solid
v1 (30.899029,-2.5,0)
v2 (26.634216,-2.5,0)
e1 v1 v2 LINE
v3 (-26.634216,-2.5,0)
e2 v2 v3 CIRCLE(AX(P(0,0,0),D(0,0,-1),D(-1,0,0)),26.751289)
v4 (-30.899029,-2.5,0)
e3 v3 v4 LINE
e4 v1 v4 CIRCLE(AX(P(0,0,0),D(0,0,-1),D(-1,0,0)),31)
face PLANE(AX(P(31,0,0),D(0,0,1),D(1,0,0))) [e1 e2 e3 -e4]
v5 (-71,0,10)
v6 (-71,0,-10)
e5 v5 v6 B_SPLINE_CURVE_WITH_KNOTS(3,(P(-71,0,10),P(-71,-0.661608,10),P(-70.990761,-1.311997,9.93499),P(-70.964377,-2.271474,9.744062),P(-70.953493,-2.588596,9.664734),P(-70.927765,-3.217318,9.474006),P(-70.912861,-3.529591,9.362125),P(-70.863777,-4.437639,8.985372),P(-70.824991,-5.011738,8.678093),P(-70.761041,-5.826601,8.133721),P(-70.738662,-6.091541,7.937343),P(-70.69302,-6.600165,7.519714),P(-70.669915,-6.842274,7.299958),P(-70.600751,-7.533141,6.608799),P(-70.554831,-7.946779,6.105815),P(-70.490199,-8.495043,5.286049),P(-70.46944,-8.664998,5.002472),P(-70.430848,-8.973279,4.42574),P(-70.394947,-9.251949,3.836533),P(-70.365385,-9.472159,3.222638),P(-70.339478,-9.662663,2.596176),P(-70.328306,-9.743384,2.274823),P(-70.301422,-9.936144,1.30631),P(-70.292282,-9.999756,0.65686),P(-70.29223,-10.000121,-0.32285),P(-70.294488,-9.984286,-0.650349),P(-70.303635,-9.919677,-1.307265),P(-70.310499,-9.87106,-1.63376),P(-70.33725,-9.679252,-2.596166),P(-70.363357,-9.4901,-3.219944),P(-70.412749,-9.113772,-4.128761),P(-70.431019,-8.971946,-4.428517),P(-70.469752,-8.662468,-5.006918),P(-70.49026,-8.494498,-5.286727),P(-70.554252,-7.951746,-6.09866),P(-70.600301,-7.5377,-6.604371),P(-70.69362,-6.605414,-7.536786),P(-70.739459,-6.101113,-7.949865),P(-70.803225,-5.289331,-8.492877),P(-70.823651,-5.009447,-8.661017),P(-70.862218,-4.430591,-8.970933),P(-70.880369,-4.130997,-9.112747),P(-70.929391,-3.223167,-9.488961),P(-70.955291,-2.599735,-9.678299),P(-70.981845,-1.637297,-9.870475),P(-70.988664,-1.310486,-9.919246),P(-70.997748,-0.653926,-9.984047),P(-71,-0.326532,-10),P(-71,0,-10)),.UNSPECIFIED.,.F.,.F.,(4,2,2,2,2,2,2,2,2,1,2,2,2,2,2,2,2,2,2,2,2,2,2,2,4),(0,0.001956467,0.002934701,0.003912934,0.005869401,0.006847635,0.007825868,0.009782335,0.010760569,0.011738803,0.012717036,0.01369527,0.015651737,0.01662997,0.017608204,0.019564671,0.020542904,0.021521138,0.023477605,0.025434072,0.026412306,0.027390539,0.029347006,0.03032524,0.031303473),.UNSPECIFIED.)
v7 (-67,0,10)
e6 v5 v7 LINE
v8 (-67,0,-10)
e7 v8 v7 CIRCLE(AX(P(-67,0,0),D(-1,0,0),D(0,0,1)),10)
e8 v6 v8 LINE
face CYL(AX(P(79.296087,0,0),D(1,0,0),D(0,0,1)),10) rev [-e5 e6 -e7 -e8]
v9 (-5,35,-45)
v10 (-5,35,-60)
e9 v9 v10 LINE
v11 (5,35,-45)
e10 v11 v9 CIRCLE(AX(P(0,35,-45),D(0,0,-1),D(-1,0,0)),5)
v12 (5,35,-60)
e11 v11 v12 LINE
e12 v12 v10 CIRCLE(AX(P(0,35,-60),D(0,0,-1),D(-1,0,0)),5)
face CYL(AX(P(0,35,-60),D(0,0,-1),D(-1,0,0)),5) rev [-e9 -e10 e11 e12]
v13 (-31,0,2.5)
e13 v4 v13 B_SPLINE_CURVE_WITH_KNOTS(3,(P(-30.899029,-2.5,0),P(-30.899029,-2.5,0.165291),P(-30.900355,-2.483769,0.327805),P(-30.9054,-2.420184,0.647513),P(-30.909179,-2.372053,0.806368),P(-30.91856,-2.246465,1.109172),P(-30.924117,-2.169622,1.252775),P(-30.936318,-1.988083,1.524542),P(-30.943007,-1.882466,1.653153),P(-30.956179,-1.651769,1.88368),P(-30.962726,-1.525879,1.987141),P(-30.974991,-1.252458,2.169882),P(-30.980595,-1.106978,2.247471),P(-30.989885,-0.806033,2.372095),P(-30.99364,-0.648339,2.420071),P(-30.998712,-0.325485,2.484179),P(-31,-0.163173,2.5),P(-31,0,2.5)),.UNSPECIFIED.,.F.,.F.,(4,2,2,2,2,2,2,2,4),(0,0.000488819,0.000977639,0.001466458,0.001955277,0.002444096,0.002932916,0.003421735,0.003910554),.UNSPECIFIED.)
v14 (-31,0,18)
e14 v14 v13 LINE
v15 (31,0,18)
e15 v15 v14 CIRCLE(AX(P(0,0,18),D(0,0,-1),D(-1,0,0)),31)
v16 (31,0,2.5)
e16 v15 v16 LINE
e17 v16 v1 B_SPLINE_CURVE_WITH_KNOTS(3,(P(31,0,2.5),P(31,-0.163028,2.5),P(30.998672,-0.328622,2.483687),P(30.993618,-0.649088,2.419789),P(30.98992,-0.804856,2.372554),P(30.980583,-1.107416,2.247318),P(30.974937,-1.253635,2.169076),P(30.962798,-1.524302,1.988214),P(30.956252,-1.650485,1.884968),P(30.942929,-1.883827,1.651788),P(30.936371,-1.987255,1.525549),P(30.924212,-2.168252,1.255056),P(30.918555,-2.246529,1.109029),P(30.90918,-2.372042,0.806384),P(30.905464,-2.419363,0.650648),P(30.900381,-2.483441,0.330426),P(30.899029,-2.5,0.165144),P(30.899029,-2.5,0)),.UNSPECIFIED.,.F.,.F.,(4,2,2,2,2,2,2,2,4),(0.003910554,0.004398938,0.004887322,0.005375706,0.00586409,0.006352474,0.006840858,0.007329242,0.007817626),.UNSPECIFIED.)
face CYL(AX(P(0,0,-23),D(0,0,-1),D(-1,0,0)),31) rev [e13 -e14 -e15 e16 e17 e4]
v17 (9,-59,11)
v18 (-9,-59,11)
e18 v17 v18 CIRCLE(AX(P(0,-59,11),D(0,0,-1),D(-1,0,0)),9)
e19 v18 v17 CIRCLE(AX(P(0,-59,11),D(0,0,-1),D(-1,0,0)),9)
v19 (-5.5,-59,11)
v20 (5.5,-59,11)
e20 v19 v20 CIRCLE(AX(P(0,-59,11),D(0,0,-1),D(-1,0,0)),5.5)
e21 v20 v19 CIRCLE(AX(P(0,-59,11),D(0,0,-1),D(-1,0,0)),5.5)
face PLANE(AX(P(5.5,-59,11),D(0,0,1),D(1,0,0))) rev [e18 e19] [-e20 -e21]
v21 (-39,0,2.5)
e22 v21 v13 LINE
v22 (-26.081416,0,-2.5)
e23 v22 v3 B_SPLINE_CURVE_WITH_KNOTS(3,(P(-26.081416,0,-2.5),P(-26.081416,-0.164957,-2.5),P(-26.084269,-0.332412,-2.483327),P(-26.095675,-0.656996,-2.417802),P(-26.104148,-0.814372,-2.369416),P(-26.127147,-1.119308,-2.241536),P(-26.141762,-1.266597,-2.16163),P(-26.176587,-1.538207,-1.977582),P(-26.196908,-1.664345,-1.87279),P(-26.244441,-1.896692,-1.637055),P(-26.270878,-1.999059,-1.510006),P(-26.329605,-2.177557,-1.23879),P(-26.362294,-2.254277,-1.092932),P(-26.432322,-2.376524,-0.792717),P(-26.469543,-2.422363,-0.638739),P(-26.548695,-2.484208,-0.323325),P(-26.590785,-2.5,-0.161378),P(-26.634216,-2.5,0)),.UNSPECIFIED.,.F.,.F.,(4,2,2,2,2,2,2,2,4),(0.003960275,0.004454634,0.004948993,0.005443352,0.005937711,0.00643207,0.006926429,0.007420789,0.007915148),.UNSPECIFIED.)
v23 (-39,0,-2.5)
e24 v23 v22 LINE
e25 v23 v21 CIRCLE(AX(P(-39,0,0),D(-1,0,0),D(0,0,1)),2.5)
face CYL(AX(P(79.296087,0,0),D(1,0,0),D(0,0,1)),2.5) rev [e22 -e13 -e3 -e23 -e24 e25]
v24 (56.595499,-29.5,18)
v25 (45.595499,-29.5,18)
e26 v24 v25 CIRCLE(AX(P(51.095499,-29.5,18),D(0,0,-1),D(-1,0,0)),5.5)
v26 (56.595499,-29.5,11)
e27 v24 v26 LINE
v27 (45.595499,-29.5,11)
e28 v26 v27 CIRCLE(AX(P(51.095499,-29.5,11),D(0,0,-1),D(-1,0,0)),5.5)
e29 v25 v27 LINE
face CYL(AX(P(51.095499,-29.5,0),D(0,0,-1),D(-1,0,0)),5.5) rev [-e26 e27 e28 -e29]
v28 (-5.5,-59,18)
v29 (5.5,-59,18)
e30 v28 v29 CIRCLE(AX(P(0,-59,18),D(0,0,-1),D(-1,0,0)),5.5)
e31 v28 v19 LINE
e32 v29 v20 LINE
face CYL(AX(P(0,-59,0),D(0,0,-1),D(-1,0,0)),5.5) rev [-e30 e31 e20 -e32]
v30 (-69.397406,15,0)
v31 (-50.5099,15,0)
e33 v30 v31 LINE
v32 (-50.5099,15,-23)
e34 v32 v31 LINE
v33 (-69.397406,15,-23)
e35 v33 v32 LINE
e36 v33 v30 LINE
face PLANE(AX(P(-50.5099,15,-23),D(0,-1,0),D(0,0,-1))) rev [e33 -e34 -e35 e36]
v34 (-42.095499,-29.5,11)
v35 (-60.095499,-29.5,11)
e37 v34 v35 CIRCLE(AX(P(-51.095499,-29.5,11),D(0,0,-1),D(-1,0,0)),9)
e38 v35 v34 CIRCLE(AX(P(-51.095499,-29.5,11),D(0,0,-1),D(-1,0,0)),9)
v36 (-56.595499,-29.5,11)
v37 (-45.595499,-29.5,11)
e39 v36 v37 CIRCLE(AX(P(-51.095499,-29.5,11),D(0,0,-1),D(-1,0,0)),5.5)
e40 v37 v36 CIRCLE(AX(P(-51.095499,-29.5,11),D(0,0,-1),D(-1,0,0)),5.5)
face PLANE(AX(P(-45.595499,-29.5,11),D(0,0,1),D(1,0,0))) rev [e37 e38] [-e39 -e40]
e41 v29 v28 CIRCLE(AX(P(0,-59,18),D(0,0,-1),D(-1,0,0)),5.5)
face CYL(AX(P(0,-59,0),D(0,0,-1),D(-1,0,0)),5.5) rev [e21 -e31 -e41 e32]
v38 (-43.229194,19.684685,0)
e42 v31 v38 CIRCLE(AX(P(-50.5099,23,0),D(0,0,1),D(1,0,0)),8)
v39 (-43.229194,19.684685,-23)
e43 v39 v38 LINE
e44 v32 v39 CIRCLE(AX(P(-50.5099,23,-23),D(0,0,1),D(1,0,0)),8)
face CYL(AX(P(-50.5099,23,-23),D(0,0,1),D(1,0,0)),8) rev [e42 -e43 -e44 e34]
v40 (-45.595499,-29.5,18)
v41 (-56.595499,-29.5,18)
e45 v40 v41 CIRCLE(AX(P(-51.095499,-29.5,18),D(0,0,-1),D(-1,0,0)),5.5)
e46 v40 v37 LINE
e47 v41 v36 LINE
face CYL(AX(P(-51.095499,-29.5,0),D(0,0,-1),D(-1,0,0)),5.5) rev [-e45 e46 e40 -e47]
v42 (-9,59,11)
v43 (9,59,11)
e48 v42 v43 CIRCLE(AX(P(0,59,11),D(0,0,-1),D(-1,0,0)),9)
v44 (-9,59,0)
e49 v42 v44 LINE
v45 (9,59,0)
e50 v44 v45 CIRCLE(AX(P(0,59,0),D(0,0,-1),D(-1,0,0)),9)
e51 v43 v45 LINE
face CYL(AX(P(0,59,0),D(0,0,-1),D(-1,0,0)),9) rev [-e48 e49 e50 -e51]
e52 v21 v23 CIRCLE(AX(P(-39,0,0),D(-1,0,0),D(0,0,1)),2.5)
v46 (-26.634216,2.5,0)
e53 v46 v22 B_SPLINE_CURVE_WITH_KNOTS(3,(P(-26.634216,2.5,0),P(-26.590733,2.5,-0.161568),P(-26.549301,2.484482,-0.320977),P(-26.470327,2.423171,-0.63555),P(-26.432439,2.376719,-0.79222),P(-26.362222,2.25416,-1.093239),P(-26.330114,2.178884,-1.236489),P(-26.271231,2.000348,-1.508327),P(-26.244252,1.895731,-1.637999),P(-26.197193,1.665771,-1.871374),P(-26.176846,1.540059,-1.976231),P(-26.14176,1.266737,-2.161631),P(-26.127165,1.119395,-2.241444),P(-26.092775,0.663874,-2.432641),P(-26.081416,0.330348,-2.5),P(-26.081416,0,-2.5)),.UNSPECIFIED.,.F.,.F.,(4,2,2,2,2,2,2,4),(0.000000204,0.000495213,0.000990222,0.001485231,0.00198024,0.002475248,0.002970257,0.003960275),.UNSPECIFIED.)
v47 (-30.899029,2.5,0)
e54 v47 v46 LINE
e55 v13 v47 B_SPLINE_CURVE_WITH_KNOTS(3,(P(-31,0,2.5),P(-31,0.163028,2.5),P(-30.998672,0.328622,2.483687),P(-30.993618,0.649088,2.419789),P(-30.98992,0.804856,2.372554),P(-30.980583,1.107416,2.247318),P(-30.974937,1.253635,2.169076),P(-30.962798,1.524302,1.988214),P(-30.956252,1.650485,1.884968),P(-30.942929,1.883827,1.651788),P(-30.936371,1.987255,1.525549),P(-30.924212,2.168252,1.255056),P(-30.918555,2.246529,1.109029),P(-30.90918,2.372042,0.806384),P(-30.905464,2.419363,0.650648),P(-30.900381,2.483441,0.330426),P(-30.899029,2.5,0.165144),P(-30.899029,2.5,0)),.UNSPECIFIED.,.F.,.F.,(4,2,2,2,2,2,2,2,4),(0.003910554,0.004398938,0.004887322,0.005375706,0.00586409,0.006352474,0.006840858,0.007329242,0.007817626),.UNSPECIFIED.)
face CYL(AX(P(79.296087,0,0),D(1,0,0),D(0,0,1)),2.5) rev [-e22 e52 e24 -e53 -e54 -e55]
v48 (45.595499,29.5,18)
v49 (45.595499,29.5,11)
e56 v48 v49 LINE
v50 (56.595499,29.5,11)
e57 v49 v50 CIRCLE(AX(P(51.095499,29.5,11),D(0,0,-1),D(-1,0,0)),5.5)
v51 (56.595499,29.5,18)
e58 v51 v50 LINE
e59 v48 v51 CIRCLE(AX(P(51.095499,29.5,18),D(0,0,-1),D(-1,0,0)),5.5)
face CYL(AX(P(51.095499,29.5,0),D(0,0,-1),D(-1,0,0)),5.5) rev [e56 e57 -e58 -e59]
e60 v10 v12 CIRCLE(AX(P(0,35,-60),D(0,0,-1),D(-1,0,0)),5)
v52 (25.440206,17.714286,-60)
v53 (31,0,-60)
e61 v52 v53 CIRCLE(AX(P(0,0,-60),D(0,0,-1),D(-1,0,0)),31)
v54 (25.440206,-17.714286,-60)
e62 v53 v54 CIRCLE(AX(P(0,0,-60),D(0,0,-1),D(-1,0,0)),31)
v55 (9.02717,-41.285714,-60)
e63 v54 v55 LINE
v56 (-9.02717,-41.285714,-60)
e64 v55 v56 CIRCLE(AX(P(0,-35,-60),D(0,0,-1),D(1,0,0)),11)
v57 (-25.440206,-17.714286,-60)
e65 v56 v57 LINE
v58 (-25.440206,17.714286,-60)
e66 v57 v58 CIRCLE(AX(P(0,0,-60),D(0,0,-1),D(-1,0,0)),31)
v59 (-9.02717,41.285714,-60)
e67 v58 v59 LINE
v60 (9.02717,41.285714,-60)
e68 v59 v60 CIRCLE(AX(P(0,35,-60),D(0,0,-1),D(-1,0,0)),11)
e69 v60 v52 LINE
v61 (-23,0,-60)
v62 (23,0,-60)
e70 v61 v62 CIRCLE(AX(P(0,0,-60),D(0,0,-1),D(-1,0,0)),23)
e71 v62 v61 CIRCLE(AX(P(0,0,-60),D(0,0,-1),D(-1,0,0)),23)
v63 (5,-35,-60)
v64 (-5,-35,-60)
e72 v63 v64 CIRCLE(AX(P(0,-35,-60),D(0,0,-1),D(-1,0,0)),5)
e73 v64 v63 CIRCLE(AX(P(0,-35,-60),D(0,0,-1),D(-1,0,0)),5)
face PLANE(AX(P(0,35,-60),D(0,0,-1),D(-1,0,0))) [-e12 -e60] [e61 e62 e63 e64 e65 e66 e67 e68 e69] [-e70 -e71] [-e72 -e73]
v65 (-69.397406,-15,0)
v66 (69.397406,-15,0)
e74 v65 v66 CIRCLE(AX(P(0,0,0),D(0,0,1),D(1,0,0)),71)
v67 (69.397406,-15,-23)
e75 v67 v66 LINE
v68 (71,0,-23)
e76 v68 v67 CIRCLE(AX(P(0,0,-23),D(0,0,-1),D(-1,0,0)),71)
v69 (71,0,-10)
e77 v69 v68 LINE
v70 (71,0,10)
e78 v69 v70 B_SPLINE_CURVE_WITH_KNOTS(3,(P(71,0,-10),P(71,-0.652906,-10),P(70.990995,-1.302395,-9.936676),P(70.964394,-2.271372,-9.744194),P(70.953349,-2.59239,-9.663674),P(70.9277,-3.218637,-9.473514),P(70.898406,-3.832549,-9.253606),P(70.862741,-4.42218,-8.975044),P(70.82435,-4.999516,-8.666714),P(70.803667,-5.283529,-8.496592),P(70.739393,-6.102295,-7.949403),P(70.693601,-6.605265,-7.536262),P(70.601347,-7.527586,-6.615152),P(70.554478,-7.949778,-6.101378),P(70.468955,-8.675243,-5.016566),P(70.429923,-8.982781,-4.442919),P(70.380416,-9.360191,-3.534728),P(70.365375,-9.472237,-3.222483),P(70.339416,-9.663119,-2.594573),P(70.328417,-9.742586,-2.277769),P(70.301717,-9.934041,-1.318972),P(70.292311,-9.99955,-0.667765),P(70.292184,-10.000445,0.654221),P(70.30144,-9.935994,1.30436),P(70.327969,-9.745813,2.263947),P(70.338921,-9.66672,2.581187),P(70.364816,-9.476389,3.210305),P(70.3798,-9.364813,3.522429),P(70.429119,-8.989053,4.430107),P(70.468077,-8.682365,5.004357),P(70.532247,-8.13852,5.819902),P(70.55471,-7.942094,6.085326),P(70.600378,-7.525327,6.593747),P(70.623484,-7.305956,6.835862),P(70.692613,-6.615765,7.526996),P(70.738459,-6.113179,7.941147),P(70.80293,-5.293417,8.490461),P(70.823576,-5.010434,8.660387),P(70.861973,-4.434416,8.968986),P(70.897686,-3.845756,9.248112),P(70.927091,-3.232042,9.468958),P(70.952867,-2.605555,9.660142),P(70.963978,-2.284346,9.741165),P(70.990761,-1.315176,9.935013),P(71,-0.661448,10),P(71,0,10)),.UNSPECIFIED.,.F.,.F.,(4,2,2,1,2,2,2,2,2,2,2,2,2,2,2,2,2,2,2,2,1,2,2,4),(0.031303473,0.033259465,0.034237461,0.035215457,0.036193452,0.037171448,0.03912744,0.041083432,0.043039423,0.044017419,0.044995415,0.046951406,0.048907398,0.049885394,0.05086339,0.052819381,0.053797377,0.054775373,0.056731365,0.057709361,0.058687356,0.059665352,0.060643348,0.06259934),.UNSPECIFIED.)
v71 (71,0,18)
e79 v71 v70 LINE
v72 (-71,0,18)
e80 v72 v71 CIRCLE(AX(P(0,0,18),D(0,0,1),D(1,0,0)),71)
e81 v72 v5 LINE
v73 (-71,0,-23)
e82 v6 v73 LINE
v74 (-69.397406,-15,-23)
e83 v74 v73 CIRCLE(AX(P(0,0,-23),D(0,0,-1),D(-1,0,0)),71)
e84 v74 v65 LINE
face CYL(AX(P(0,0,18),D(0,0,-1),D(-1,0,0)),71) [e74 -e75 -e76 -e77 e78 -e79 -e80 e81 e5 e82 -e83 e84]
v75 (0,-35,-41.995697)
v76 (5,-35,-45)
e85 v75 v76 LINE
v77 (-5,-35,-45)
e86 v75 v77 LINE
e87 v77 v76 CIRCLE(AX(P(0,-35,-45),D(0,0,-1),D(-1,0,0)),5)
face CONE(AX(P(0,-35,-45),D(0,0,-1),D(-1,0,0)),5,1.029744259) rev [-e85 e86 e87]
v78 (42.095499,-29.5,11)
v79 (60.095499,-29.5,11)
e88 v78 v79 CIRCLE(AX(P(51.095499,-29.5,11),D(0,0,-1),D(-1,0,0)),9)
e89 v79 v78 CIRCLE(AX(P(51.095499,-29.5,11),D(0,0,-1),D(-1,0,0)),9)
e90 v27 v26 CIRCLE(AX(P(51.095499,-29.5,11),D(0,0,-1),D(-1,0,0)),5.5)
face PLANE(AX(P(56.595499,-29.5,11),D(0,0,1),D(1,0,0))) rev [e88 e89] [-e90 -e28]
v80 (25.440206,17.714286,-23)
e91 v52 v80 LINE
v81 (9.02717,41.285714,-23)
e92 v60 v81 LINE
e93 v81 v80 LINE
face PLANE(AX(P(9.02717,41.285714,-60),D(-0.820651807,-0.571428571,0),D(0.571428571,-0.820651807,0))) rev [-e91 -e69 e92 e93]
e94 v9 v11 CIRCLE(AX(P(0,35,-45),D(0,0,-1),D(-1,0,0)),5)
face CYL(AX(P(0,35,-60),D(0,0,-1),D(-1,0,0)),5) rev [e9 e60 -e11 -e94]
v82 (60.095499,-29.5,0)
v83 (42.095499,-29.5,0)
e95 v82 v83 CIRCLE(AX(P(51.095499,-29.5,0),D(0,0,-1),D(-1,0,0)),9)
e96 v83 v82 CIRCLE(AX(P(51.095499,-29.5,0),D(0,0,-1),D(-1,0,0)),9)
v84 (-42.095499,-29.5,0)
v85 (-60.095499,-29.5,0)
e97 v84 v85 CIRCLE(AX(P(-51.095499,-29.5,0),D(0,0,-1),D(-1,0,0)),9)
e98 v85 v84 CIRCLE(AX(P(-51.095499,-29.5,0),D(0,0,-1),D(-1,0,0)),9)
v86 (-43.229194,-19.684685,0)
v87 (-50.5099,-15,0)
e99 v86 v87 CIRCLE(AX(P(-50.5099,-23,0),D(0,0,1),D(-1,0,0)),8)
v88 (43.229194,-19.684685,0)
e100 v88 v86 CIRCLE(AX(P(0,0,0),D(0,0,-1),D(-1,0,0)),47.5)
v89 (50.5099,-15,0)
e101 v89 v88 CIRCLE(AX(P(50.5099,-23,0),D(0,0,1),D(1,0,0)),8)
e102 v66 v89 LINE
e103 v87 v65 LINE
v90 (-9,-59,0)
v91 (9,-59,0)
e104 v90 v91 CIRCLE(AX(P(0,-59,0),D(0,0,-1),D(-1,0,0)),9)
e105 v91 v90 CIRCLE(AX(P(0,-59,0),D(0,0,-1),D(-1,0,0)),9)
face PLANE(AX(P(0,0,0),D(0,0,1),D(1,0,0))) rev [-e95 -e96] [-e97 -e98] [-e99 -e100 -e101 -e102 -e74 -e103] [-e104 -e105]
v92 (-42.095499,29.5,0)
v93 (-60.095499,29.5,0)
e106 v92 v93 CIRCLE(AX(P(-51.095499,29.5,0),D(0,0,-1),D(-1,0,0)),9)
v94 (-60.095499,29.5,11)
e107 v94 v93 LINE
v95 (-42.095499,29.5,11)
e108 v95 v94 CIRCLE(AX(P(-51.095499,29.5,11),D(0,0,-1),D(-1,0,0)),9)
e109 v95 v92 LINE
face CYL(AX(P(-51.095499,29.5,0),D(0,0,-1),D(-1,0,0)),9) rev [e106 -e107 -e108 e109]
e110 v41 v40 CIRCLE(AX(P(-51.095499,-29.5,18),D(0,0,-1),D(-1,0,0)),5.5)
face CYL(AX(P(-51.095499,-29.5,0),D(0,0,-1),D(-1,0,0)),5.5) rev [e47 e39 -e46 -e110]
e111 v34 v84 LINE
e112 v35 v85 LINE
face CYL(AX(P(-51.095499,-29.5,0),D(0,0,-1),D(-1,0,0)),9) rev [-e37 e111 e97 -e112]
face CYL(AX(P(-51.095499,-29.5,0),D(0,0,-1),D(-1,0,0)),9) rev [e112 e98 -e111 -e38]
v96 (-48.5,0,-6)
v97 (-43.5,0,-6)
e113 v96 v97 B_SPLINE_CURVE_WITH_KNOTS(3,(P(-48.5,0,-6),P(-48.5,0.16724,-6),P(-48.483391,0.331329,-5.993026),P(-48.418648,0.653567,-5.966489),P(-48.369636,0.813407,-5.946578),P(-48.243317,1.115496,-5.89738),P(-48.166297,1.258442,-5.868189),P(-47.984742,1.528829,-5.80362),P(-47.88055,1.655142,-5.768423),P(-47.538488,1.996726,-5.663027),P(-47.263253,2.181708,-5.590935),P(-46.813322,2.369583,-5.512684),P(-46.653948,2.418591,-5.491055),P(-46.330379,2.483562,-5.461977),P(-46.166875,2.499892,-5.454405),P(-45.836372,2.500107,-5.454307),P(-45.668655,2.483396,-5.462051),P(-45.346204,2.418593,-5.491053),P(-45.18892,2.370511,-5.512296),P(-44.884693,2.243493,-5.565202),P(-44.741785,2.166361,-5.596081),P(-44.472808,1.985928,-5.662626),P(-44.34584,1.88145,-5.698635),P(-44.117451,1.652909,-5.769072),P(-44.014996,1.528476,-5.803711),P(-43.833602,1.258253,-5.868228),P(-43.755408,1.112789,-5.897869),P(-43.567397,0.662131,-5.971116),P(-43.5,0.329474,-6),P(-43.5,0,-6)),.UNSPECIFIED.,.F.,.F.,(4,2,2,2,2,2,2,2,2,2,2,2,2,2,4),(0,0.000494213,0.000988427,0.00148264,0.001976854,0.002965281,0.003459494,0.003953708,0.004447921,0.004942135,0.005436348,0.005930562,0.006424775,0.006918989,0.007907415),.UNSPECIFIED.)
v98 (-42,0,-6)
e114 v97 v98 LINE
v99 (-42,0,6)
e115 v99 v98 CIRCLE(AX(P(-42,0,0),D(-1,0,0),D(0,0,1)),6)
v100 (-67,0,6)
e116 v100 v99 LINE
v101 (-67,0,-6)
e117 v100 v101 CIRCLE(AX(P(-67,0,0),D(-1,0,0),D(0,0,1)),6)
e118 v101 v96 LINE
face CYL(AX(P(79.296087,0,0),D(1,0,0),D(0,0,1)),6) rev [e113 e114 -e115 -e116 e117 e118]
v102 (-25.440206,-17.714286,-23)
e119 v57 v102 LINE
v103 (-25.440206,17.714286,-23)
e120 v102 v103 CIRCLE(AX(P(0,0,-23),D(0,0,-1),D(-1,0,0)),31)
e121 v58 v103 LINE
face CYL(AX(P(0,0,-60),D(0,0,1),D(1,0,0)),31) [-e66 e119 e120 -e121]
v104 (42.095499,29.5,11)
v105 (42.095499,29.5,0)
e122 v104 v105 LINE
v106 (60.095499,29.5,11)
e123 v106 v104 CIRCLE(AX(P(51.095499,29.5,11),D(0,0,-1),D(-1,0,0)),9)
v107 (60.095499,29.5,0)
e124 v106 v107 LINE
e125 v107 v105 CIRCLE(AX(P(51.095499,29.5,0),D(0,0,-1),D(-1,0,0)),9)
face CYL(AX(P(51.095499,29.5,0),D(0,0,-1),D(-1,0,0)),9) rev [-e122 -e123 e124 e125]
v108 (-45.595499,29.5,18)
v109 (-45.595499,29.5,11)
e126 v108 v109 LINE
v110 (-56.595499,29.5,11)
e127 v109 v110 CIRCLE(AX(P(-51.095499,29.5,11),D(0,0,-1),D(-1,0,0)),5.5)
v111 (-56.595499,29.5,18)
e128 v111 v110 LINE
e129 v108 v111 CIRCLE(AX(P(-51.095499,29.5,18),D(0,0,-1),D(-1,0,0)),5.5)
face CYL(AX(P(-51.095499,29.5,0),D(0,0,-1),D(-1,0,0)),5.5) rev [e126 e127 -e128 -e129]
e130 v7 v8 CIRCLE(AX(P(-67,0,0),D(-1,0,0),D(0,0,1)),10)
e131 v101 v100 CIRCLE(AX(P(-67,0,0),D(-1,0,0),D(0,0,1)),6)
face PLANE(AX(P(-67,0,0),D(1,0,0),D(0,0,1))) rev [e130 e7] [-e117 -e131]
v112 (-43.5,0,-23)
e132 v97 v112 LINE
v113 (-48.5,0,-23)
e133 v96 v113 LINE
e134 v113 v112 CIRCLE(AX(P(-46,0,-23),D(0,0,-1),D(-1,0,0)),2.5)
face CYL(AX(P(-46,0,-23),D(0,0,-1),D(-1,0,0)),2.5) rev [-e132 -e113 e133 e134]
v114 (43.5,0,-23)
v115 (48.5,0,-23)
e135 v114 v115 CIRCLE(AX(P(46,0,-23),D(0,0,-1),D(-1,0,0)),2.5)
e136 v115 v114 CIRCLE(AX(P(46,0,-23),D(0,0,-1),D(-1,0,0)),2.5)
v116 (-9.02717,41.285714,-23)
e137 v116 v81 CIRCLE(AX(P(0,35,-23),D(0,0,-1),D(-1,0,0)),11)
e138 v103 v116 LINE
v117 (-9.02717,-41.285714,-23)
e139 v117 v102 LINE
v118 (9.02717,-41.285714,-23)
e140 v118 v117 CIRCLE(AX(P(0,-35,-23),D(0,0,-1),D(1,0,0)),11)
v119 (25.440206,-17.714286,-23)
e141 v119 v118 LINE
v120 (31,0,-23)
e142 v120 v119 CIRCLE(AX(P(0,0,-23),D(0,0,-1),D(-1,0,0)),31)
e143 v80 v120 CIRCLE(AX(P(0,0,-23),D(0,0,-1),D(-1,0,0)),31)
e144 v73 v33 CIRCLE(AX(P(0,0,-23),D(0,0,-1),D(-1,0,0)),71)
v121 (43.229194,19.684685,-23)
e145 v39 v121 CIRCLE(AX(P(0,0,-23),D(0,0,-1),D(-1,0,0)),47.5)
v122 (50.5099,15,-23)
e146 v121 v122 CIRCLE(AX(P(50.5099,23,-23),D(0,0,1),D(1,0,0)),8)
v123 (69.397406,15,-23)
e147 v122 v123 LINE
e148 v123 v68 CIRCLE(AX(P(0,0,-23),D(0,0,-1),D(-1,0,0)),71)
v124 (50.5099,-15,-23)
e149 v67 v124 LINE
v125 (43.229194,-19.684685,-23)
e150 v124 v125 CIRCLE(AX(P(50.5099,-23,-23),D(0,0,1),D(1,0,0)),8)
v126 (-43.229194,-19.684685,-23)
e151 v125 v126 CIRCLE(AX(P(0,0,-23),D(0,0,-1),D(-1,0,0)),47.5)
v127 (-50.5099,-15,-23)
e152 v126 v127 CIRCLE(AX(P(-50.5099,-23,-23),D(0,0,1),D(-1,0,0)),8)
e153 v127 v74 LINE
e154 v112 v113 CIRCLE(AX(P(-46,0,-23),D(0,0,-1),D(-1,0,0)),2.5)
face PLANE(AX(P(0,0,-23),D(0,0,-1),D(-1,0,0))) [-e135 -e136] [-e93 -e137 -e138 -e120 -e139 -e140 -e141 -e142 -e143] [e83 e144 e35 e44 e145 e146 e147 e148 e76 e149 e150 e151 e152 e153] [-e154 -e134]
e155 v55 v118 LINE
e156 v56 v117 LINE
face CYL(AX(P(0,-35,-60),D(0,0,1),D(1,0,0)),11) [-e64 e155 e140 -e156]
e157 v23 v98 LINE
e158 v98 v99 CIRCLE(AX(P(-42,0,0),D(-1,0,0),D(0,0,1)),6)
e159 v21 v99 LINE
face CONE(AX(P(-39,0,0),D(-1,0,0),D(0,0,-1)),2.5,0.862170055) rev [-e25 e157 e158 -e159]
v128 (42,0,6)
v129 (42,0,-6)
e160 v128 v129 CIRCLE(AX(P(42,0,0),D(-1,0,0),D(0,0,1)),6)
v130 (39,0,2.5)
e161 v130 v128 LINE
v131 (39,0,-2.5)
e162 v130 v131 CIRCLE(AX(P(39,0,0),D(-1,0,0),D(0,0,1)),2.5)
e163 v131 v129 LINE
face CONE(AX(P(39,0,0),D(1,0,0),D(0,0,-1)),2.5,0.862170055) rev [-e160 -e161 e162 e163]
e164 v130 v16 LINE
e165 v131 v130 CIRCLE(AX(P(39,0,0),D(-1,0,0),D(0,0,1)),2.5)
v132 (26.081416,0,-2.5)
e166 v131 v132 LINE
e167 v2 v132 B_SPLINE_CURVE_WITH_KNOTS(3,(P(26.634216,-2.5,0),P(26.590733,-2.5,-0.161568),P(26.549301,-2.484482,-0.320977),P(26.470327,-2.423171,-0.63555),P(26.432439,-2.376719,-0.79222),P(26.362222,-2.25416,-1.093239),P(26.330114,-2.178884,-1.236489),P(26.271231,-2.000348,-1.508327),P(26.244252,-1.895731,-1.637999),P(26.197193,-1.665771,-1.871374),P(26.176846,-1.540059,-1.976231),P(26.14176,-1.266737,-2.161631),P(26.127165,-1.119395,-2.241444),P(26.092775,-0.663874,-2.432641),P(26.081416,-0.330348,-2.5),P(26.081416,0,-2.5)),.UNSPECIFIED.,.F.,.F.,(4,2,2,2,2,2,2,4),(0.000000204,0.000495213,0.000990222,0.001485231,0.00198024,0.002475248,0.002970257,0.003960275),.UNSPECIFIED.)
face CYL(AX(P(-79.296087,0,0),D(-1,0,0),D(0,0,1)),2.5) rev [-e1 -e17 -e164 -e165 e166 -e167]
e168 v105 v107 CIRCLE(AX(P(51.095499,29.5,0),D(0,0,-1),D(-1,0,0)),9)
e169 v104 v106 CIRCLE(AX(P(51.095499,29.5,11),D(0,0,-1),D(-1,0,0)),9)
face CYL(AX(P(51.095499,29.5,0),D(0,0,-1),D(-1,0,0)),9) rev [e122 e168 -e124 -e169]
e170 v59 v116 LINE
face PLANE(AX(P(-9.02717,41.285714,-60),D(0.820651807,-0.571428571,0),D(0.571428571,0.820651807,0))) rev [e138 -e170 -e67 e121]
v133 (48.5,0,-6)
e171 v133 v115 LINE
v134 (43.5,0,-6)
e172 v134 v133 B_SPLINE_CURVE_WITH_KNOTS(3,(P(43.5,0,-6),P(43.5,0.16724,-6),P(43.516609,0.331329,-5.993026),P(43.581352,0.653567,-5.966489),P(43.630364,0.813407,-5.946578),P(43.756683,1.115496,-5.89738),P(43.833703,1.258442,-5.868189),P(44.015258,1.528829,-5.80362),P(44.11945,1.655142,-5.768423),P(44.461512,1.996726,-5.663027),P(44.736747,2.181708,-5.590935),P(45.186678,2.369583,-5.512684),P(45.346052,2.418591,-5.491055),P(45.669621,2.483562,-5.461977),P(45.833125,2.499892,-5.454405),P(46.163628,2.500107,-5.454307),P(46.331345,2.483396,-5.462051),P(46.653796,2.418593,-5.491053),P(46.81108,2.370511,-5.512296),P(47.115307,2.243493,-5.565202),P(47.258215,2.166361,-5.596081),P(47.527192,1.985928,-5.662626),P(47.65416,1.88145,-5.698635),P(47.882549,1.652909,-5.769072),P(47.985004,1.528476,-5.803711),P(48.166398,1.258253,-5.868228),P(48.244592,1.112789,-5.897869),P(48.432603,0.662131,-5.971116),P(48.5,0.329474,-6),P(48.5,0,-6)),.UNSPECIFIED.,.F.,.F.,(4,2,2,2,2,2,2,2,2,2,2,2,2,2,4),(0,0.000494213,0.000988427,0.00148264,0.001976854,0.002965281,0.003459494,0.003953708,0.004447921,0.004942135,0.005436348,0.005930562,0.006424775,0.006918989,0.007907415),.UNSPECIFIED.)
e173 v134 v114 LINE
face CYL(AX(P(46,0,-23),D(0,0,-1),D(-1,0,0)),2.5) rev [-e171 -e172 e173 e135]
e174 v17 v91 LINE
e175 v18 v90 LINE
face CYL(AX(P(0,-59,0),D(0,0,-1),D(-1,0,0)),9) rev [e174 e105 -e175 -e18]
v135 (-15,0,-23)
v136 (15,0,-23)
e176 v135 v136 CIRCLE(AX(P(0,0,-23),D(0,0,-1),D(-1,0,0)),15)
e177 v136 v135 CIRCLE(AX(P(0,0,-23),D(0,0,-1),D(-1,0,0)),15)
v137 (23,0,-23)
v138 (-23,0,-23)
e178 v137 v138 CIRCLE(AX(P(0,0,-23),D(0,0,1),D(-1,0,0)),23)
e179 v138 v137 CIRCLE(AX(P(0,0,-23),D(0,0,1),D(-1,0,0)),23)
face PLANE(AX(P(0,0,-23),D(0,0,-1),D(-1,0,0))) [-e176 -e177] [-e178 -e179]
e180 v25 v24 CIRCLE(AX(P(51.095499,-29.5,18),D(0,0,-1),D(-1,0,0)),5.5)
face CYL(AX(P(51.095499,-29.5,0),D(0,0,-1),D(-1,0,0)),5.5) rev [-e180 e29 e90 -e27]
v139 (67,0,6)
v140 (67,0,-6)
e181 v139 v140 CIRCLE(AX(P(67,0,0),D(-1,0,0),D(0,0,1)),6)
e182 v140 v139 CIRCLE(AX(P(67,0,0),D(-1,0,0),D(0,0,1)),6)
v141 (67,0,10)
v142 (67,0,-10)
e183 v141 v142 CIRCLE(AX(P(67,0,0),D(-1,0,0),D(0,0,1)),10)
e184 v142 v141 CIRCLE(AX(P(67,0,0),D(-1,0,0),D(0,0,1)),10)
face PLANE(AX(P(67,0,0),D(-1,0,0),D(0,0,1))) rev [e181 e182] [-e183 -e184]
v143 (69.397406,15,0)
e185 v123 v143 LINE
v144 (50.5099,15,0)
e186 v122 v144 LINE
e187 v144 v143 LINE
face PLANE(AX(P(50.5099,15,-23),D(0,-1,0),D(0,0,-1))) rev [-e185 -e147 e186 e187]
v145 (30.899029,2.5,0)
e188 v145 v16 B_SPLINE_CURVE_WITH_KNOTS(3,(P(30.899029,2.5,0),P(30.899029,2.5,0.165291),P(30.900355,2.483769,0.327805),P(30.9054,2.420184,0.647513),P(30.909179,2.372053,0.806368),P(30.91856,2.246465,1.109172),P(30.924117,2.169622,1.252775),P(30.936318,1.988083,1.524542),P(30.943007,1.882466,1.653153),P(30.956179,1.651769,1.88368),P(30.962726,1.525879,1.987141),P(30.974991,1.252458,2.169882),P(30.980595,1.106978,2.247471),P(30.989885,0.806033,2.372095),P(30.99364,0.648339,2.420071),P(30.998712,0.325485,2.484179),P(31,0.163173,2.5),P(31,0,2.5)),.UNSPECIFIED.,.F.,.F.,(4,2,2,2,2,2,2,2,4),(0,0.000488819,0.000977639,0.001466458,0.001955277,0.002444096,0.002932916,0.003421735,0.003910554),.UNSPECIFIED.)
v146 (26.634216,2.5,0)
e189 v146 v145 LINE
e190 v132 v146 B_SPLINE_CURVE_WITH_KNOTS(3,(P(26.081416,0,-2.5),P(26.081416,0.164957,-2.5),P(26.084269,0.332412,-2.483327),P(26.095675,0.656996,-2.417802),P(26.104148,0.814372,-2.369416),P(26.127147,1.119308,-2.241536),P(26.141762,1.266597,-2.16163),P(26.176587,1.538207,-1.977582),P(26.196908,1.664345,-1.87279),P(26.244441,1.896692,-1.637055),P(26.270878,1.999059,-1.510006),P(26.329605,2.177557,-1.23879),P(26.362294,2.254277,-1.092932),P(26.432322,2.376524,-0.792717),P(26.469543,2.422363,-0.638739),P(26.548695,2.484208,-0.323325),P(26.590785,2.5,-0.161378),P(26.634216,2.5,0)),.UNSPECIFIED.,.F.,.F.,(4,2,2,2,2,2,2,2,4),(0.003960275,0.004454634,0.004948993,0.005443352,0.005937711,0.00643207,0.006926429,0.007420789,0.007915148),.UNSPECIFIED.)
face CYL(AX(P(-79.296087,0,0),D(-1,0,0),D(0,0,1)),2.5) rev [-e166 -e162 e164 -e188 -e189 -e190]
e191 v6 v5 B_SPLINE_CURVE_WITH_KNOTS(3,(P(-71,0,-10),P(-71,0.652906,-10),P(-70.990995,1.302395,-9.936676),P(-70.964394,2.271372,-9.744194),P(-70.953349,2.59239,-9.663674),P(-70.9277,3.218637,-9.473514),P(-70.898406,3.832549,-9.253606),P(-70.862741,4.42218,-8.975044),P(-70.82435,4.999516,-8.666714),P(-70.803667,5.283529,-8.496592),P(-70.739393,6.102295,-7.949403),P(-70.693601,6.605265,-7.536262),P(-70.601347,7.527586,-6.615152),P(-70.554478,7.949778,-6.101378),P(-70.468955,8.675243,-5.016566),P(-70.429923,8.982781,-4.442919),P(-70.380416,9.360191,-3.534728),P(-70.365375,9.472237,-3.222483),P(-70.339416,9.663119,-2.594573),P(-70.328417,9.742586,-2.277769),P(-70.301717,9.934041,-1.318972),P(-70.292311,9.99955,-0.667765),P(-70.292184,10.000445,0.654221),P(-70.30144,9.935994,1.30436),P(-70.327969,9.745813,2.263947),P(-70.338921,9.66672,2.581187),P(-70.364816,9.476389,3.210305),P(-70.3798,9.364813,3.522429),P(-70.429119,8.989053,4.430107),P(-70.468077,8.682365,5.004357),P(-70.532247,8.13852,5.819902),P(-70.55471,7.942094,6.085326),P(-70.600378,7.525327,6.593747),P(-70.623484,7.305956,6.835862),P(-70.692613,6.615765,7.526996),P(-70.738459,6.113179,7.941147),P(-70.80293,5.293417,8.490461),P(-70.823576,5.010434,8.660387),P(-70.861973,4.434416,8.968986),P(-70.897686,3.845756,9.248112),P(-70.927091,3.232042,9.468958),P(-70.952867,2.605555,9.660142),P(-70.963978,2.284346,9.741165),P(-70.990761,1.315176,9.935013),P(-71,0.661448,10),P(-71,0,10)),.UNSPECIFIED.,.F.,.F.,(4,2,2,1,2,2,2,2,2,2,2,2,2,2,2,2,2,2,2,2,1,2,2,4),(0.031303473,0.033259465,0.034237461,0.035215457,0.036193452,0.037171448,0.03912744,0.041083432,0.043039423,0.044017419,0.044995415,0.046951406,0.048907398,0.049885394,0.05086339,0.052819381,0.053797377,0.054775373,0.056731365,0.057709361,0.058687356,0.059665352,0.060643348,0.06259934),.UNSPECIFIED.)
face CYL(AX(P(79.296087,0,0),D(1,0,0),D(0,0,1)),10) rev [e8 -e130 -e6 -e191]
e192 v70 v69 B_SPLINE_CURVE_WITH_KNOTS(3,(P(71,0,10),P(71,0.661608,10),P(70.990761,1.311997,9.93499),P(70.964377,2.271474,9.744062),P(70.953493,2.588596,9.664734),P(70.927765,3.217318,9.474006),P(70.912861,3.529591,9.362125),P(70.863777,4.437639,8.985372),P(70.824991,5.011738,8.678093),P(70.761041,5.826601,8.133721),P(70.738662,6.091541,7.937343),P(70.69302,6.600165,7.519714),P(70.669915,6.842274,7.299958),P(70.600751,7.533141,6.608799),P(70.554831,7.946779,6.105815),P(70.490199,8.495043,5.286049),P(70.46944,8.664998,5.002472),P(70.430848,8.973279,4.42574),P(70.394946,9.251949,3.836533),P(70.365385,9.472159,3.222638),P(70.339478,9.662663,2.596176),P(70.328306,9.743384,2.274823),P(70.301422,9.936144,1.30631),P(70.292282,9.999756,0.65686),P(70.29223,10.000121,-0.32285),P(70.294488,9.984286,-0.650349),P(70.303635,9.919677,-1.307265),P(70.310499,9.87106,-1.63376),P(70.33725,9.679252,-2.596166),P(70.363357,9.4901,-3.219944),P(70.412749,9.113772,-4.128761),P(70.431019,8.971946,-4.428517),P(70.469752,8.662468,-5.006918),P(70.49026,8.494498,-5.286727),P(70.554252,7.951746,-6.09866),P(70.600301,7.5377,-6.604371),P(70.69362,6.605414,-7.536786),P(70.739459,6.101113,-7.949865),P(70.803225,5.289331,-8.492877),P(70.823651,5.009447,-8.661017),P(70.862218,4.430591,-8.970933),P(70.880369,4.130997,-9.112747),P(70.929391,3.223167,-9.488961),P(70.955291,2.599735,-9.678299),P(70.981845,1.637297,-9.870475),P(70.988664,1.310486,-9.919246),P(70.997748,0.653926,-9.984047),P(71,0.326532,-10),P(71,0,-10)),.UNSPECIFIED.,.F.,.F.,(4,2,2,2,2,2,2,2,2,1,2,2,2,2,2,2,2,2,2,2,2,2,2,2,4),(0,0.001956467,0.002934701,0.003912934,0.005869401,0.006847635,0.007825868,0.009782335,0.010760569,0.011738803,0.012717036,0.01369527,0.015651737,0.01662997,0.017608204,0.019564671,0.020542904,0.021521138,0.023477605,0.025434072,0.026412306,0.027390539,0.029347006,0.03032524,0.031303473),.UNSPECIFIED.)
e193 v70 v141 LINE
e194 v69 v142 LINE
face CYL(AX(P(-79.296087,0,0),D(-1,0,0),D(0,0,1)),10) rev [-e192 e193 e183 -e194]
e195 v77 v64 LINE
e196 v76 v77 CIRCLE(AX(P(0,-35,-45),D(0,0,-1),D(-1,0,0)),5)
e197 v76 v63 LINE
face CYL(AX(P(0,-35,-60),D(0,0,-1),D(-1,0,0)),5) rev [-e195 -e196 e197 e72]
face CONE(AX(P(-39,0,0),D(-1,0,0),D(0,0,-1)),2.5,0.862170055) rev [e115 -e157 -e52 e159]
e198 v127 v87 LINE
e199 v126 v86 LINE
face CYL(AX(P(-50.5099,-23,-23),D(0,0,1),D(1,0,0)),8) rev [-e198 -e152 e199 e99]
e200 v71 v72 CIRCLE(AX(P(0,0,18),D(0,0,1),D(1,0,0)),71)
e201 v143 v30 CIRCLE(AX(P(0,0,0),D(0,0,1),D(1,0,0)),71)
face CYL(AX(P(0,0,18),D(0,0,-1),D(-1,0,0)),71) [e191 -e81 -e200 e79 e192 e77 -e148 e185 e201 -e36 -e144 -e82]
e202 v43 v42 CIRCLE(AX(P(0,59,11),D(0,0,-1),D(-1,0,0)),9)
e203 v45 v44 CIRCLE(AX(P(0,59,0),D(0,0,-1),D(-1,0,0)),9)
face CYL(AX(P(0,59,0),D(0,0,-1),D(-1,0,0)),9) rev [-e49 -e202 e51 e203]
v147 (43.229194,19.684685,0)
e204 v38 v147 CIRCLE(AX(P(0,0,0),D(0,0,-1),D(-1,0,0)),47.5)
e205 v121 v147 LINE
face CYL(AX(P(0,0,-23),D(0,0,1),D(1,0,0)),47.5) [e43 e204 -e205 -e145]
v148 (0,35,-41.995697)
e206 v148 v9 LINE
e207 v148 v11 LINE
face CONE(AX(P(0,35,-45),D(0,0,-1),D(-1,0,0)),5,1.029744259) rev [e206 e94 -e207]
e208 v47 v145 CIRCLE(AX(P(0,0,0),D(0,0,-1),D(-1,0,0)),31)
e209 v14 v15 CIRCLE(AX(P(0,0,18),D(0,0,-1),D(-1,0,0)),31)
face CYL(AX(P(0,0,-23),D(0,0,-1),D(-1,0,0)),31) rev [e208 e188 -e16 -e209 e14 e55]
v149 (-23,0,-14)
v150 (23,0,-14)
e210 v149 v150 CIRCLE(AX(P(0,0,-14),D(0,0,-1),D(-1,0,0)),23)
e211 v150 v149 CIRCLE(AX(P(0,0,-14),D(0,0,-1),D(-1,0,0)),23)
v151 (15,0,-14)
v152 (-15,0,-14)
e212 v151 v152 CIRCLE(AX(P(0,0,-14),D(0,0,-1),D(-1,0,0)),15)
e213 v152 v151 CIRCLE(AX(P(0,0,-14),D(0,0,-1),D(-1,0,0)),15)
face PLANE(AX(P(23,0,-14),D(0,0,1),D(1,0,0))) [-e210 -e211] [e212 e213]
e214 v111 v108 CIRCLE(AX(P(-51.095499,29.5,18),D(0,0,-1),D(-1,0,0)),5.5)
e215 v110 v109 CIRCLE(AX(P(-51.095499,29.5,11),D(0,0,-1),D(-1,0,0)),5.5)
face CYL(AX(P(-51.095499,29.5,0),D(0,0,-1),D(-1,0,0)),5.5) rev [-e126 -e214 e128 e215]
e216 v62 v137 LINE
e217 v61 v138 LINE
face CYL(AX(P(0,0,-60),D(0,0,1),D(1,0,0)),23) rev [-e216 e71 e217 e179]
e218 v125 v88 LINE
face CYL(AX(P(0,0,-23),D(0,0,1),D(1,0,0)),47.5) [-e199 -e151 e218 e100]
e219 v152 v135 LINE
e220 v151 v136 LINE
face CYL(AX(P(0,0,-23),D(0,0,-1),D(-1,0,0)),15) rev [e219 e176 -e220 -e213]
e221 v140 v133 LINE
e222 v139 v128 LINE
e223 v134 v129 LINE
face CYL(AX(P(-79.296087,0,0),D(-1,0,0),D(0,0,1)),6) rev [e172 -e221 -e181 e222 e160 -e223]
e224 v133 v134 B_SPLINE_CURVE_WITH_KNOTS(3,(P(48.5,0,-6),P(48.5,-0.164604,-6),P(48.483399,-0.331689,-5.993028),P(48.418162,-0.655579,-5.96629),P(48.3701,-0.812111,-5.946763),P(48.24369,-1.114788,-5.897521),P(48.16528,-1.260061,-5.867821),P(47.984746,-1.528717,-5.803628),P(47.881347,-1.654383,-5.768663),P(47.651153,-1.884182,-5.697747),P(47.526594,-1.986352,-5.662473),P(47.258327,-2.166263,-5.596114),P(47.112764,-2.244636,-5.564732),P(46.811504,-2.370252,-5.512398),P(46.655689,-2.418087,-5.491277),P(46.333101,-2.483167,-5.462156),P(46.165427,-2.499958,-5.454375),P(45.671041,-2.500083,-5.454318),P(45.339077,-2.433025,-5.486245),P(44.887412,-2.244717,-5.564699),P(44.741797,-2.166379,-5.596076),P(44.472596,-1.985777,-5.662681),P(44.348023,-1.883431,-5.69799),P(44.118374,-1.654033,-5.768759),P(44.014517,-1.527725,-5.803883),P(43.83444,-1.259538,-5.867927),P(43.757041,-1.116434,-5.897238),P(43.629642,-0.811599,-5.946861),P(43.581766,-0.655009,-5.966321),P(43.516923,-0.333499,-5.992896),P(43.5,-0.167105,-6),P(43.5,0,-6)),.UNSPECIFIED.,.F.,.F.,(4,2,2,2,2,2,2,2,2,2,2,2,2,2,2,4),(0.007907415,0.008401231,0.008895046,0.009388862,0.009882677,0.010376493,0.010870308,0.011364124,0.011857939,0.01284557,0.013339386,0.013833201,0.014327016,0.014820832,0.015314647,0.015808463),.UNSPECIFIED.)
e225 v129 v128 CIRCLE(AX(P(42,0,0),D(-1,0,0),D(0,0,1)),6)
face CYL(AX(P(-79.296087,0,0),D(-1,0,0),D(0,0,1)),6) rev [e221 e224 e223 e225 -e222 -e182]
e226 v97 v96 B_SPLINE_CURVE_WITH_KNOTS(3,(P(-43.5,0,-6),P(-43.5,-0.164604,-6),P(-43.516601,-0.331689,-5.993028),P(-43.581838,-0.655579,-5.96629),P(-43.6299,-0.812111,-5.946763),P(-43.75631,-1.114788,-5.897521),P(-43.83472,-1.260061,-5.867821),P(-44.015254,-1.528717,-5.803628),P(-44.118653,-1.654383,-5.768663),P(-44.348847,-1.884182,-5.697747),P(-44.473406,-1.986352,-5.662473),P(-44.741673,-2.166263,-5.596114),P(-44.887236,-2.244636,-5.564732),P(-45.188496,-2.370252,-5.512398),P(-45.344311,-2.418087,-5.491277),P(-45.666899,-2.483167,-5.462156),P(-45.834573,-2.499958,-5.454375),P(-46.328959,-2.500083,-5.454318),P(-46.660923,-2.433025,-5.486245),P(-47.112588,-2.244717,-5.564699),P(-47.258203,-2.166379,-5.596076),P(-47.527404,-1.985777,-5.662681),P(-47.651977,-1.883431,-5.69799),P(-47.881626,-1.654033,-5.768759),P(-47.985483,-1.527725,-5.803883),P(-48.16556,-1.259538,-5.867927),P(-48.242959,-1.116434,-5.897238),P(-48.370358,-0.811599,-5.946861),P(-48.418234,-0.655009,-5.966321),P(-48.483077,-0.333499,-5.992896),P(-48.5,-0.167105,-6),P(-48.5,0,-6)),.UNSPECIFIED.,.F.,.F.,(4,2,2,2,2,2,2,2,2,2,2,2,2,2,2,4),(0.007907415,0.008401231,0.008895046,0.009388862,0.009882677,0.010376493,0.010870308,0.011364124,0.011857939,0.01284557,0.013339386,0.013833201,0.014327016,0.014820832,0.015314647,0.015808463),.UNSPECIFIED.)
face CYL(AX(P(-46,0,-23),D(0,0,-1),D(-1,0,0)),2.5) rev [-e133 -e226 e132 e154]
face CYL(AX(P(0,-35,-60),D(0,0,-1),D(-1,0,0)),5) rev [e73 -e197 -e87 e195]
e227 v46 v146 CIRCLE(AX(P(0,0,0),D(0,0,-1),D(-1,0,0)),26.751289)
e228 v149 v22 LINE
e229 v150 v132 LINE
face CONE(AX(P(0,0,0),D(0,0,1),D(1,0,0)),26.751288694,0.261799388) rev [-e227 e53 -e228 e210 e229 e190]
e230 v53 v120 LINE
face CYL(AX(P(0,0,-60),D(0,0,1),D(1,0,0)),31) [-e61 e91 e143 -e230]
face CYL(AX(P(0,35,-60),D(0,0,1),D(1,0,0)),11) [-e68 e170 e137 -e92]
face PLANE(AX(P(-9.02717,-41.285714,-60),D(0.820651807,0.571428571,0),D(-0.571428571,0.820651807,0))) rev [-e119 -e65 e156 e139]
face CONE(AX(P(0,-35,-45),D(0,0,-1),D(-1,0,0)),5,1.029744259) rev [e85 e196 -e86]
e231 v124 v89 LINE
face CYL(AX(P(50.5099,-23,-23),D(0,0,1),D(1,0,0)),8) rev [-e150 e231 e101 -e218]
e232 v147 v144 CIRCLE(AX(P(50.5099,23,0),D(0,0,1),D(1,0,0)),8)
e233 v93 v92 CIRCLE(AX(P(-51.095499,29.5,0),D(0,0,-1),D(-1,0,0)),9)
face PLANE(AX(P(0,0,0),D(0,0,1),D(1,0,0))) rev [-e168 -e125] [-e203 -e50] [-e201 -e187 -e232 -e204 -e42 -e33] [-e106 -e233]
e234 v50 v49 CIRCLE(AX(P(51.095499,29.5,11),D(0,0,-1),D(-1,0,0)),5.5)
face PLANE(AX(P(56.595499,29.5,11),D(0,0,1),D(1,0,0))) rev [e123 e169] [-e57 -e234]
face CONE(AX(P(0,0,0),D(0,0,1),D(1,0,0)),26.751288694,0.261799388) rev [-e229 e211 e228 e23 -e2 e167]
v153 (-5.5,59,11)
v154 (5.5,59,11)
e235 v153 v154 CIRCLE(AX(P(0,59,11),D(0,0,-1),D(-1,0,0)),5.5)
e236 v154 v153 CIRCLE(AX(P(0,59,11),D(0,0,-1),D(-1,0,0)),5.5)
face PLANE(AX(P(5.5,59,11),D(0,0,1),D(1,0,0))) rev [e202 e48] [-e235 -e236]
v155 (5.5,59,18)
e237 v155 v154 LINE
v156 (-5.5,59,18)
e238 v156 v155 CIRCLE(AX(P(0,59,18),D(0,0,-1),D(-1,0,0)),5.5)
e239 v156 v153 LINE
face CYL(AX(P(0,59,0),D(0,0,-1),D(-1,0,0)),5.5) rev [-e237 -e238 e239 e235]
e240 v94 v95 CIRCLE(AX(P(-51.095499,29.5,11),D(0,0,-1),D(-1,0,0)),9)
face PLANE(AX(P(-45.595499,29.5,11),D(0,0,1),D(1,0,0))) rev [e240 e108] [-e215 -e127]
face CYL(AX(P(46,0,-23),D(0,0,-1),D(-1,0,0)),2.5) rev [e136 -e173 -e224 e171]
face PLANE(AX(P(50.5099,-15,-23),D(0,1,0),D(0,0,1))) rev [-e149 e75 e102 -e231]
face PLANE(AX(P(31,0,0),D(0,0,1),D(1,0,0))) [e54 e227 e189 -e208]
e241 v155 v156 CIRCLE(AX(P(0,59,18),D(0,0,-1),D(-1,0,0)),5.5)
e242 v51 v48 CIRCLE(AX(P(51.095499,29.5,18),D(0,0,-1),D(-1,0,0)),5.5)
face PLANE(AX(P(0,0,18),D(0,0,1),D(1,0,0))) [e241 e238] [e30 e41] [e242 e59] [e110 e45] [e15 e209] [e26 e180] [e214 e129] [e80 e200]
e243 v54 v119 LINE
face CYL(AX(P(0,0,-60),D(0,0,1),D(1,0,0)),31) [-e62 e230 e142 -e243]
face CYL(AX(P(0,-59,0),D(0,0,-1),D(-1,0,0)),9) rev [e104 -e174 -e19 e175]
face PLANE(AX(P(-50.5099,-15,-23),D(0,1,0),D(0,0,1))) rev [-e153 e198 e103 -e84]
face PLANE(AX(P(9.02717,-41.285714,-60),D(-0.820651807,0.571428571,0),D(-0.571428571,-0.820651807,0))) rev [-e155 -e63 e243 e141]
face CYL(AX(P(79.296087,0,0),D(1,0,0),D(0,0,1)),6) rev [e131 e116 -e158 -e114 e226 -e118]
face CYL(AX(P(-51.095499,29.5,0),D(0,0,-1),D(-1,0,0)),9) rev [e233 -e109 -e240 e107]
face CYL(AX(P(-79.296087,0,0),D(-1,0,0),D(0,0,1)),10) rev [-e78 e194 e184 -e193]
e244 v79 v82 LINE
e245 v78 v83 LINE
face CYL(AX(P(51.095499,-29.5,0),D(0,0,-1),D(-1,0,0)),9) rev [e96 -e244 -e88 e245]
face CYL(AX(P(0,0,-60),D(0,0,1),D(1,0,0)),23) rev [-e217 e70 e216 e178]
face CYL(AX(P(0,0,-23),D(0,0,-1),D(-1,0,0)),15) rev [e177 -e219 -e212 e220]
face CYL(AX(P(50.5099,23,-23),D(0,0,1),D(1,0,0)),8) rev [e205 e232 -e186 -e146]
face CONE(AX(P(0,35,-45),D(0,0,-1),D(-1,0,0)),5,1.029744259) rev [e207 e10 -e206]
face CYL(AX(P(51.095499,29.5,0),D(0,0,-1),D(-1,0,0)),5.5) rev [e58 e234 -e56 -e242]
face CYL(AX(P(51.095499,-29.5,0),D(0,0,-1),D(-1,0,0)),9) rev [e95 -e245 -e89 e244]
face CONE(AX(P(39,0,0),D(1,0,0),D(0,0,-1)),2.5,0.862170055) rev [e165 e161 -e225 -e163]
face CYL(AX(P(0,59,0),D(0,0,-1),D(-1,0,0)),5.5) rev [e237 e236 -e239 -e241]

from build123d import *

# Parameters (mm, degrees)
BASE_FLANGE_SKETCH_R                   = 71
BASE_FLANGE_142_DEPTH                  = 18
MIDDLE_START                           = 23
MIDDLE_BOSS_DEPTH                      = 23
OVAL_FLANGE_SKETCH_R                   = 23
OVAL_TOP_FLANGE_DEPTH                  = 37
COUNTERBORED_BOLT_HOLE_M10_D           = 11
COUNTERBORED_BOLT_HOLE_M10_CBORE_D     = 18
COUNTERBORED_BOLT_HOLE_M10_CBORE_DEPTH = 11
BOLT_HOLE_PATTERN_6X_COUNT             = 6
CLEARANCE_HOLE_M5_D                    = 5
CLEARANCE_HOLE_M5_DEPTH                = 18
CLEARANCE_HOLE_M5_TIP                  = 1.502151548
TAPPED_HOLE_M10X1_0_D                  = 10
TAPPED_HOLE_M10X1_0_DEPTH              = 15
TAPPED_HOLE_M10X1_0_TIP                = 3.004303095


with BuildPart() as part:
    # Base Flange Sketch → Base Flange Ø142 (new body)
    with BuildSketch(Plane.XY):
        Circle(BASE_FLANGE_SKETCH_R)
    extrude(amount=BASE_FLANGE_142_DEPTH)

    # Middle Boss Sketch → Middle Boss (add)
    with BuildSketch(Plane(origin=(0, 0, 0), x_dir=(-1, 0, 0), z_dir=(0, 0, -1)).offset(MIDDLE_START)):
        with BuildLine():
            Line((50.50990002, 15), (69.397406292, 15))
            ThreePointArc((69.397406292, 15), (71, 0), (69.397406292, -15))
            Line((69.397406292, -15), (50.50990002, -15))
            ThreePointArc((50.50990002, -15), (46.181073535, -16.272350986), (43.229193711, -19.684684685))
            ThreePointArc((43.229193711, -19.684684685), (0, -47.5), (-43.229193711, -19.684684685))
            ThreePointArc((-43.229193711, -19.684684685), (-46.181073535, -16.272350986), (-50.50990002, -15))
            Line((-50.50990002, -15), (-69.397406292, -15))
            ThreePointArc((-69.397406292, -15), (-71, 0), (-69.397406292, 15))
            Line((-69.397406292, 15), (-50.50990002, 15))
            ThreePointArc((-50.50990002, 15), (-46.181073535, 16.272350986), (-43.229193711, 19.684684685))
            ThreePointArc((-43.229193711, 19.684684685), (0, 47.5), (43.229193711, 19.684684685))
            ThreePointArc((43.229193711, 19.684684685), (46.181073535, 16.272350986), (50.50990002, 15))
        make_face()
    extrude(amount=-MIDDLE_BOSS_DEPTH)

    # Oval Flange Sketch → Oval Top Flange (add)
    with BuildSketch(Plane(origin=(0, 0, -23), x_dir=(-1, 0, 0), z_dir=(0, 0, -1))):
        with BuildLine():
            Line((-9.027169873, 41.285714286), (-25.440206006, 17.714285714))
            ThreePointArc((-25.440206006, 17.714285714), (-31, 0), (-25.440206006, -17.714285714))
            Line((-25.440206006, -17.714285714), (-9.027169873, -41.285714286))
            ThreePointArc((-9.027169873, -41.285714286), (0, -46), (9.027169873, -41.285714286))
            Line((9.027169873, -41.285714286), (25.440206006, -17.714285714))
            ThreePointArc((25.440206006, -17.714285714), (31, 0), (25.440206006, 17.714285714))
            Line((25.440206006, 17.714285714), (9.027169873, 41.285714286))
            ThreePointArc((9.027169873, 41.285714286), (0, 46), (-9.027169873, 41.285714286))
        make_face()
        Circle(OVAL_FLANGE_SKETCH_R, mode=Mode.SUBTRACT)
    extrude(amount=OVAL_TOP_FLANGE_DEPTH)

    # Counterbored Bolt Hole M10 (through all)
    with Locations(Plane(origin=(0, 0, 0), x_dir=(-1, 0, 0), z_dir=(0, 0, -1))):
        with Locations((0, -59)):
            counterbored_bolt_hole_m10 = CounterBoreHole(COUNTERBORED_BOLT_HOLE_M10_D / 2, COUNTERBORED_BOLT_HOLE_M10_CBORE_D / 2, COUNTERBORED_BOLT_HOLE_M10_CBORE_DEPTH)

    # Bolt Hole Pattern 6x: Counterbored Bolt Hole M10 ×6 about axis
    bolt_hole_pattern_6x_axis = Axis((0, 0, 0), (0, 0, 1))
    for i in range(1, BOLT_HOLE_PATTERN_6X_COUNT):
        add(counterbored_bolt_hole_m10.rotate(bolt_hole_pattern_6x_axis, i * 360 / BOLT_HOLE_PATTERN_6X_COUNT), mode=Mode.SUBTRACT)

    # Central Bore Profile → Central Bore (revolve, cut)
    with BuildSketch(Plane(origin=(0, 0, 0), x_dir=(1, 0, 0), z_dir=(0, 1, 0)), mode=Mode.PRIVATE) as central_bore_sk:
        Polygon((0, 23), (0, -18), (31, -18), (31, 0), (26.751288694, 0), (23, 14), (15, 14), (15, 23), align=None)
    revolve(central_bore_sk.sketch.rotate(Axis((0, 0, -23), (0, 0, 1)), 180), axis=Axis((0, 0, -23), (0, 0, 1)), mode=Mode.SUBTRACT)

    # Side Port Profile → Side Port (revolve, cut)
    with BuildSketch(Plane(origin=(0, 0, 0), x_dir=(1, 0, 0), z_dir=(0, 1, 0))):
        Polygon((15.299257969, -2.5), (15.299257969, 0), (71, 0), (71, -10), (67, -10), (67, -6), (42, -6), (39, -2.5), align=None)
    side_port = revolve(axis=Axis((-79.296087495, 0, 0), (1, 0, 0)), mode=Mode.SUBTRACT)

    # Side Port Mirror: Side Port across plane
    add(side_port.mirror(Plane(origin=(0, 0, 0), x_dir=(0, 0, 1), z_dir=(1, 0, 0))), mode=Mode.SUBTRACT)

    # Clearance Hole M5
    with Locations(Plane(origin=(0, 0, -23), x_dir=(-1, 0, 0), z_dir=(0, 0, -1))):
        with Locations((-46, 0), (46, 0)):
            Hole(CLEARANCE_HOLE_M5_D / 2, depth=CLEARANCE_HOLE_M5_DEPTH)
            with Locations((0, 0, -(CLEARANCE_HOLE_M5_DEPTH + CLEARANCE_HOLE_M5_TIP / 2))):  # 118° drill point
                Cone(0, CLEARANCE_HOLE_M5_D / 2, CLEARANCE_HOLE_M5_TIP, mode=Mode.SUBTRACT)

    # Tapped Hole M10x1.0
    with Locations(Plane(origin=(0, 0, -60), x_dir=(-1, 0, 0), z_dir=(0, 0, -1))):
        with Locations((0, -35), (0, 35)):
            Hole(TAPPED_HOLE_M10X1_0_D / 2, depth=TAPPED_HOLE_M10X1_0_DEPTH)
            with Locations((0, 0, -(TAPPED_HOLE_M10X1_0_DEPTH + TAPPED_HOLE_M10X1_0_TIP / 2))):  # 118° drill point
                Cone(0, TAPPED_HOLE_M10X1_0_D / 2, TAPPED_HOLE_M10X1_0_TIP, mode=Mode.SUBTRACT)


solid = part.part
